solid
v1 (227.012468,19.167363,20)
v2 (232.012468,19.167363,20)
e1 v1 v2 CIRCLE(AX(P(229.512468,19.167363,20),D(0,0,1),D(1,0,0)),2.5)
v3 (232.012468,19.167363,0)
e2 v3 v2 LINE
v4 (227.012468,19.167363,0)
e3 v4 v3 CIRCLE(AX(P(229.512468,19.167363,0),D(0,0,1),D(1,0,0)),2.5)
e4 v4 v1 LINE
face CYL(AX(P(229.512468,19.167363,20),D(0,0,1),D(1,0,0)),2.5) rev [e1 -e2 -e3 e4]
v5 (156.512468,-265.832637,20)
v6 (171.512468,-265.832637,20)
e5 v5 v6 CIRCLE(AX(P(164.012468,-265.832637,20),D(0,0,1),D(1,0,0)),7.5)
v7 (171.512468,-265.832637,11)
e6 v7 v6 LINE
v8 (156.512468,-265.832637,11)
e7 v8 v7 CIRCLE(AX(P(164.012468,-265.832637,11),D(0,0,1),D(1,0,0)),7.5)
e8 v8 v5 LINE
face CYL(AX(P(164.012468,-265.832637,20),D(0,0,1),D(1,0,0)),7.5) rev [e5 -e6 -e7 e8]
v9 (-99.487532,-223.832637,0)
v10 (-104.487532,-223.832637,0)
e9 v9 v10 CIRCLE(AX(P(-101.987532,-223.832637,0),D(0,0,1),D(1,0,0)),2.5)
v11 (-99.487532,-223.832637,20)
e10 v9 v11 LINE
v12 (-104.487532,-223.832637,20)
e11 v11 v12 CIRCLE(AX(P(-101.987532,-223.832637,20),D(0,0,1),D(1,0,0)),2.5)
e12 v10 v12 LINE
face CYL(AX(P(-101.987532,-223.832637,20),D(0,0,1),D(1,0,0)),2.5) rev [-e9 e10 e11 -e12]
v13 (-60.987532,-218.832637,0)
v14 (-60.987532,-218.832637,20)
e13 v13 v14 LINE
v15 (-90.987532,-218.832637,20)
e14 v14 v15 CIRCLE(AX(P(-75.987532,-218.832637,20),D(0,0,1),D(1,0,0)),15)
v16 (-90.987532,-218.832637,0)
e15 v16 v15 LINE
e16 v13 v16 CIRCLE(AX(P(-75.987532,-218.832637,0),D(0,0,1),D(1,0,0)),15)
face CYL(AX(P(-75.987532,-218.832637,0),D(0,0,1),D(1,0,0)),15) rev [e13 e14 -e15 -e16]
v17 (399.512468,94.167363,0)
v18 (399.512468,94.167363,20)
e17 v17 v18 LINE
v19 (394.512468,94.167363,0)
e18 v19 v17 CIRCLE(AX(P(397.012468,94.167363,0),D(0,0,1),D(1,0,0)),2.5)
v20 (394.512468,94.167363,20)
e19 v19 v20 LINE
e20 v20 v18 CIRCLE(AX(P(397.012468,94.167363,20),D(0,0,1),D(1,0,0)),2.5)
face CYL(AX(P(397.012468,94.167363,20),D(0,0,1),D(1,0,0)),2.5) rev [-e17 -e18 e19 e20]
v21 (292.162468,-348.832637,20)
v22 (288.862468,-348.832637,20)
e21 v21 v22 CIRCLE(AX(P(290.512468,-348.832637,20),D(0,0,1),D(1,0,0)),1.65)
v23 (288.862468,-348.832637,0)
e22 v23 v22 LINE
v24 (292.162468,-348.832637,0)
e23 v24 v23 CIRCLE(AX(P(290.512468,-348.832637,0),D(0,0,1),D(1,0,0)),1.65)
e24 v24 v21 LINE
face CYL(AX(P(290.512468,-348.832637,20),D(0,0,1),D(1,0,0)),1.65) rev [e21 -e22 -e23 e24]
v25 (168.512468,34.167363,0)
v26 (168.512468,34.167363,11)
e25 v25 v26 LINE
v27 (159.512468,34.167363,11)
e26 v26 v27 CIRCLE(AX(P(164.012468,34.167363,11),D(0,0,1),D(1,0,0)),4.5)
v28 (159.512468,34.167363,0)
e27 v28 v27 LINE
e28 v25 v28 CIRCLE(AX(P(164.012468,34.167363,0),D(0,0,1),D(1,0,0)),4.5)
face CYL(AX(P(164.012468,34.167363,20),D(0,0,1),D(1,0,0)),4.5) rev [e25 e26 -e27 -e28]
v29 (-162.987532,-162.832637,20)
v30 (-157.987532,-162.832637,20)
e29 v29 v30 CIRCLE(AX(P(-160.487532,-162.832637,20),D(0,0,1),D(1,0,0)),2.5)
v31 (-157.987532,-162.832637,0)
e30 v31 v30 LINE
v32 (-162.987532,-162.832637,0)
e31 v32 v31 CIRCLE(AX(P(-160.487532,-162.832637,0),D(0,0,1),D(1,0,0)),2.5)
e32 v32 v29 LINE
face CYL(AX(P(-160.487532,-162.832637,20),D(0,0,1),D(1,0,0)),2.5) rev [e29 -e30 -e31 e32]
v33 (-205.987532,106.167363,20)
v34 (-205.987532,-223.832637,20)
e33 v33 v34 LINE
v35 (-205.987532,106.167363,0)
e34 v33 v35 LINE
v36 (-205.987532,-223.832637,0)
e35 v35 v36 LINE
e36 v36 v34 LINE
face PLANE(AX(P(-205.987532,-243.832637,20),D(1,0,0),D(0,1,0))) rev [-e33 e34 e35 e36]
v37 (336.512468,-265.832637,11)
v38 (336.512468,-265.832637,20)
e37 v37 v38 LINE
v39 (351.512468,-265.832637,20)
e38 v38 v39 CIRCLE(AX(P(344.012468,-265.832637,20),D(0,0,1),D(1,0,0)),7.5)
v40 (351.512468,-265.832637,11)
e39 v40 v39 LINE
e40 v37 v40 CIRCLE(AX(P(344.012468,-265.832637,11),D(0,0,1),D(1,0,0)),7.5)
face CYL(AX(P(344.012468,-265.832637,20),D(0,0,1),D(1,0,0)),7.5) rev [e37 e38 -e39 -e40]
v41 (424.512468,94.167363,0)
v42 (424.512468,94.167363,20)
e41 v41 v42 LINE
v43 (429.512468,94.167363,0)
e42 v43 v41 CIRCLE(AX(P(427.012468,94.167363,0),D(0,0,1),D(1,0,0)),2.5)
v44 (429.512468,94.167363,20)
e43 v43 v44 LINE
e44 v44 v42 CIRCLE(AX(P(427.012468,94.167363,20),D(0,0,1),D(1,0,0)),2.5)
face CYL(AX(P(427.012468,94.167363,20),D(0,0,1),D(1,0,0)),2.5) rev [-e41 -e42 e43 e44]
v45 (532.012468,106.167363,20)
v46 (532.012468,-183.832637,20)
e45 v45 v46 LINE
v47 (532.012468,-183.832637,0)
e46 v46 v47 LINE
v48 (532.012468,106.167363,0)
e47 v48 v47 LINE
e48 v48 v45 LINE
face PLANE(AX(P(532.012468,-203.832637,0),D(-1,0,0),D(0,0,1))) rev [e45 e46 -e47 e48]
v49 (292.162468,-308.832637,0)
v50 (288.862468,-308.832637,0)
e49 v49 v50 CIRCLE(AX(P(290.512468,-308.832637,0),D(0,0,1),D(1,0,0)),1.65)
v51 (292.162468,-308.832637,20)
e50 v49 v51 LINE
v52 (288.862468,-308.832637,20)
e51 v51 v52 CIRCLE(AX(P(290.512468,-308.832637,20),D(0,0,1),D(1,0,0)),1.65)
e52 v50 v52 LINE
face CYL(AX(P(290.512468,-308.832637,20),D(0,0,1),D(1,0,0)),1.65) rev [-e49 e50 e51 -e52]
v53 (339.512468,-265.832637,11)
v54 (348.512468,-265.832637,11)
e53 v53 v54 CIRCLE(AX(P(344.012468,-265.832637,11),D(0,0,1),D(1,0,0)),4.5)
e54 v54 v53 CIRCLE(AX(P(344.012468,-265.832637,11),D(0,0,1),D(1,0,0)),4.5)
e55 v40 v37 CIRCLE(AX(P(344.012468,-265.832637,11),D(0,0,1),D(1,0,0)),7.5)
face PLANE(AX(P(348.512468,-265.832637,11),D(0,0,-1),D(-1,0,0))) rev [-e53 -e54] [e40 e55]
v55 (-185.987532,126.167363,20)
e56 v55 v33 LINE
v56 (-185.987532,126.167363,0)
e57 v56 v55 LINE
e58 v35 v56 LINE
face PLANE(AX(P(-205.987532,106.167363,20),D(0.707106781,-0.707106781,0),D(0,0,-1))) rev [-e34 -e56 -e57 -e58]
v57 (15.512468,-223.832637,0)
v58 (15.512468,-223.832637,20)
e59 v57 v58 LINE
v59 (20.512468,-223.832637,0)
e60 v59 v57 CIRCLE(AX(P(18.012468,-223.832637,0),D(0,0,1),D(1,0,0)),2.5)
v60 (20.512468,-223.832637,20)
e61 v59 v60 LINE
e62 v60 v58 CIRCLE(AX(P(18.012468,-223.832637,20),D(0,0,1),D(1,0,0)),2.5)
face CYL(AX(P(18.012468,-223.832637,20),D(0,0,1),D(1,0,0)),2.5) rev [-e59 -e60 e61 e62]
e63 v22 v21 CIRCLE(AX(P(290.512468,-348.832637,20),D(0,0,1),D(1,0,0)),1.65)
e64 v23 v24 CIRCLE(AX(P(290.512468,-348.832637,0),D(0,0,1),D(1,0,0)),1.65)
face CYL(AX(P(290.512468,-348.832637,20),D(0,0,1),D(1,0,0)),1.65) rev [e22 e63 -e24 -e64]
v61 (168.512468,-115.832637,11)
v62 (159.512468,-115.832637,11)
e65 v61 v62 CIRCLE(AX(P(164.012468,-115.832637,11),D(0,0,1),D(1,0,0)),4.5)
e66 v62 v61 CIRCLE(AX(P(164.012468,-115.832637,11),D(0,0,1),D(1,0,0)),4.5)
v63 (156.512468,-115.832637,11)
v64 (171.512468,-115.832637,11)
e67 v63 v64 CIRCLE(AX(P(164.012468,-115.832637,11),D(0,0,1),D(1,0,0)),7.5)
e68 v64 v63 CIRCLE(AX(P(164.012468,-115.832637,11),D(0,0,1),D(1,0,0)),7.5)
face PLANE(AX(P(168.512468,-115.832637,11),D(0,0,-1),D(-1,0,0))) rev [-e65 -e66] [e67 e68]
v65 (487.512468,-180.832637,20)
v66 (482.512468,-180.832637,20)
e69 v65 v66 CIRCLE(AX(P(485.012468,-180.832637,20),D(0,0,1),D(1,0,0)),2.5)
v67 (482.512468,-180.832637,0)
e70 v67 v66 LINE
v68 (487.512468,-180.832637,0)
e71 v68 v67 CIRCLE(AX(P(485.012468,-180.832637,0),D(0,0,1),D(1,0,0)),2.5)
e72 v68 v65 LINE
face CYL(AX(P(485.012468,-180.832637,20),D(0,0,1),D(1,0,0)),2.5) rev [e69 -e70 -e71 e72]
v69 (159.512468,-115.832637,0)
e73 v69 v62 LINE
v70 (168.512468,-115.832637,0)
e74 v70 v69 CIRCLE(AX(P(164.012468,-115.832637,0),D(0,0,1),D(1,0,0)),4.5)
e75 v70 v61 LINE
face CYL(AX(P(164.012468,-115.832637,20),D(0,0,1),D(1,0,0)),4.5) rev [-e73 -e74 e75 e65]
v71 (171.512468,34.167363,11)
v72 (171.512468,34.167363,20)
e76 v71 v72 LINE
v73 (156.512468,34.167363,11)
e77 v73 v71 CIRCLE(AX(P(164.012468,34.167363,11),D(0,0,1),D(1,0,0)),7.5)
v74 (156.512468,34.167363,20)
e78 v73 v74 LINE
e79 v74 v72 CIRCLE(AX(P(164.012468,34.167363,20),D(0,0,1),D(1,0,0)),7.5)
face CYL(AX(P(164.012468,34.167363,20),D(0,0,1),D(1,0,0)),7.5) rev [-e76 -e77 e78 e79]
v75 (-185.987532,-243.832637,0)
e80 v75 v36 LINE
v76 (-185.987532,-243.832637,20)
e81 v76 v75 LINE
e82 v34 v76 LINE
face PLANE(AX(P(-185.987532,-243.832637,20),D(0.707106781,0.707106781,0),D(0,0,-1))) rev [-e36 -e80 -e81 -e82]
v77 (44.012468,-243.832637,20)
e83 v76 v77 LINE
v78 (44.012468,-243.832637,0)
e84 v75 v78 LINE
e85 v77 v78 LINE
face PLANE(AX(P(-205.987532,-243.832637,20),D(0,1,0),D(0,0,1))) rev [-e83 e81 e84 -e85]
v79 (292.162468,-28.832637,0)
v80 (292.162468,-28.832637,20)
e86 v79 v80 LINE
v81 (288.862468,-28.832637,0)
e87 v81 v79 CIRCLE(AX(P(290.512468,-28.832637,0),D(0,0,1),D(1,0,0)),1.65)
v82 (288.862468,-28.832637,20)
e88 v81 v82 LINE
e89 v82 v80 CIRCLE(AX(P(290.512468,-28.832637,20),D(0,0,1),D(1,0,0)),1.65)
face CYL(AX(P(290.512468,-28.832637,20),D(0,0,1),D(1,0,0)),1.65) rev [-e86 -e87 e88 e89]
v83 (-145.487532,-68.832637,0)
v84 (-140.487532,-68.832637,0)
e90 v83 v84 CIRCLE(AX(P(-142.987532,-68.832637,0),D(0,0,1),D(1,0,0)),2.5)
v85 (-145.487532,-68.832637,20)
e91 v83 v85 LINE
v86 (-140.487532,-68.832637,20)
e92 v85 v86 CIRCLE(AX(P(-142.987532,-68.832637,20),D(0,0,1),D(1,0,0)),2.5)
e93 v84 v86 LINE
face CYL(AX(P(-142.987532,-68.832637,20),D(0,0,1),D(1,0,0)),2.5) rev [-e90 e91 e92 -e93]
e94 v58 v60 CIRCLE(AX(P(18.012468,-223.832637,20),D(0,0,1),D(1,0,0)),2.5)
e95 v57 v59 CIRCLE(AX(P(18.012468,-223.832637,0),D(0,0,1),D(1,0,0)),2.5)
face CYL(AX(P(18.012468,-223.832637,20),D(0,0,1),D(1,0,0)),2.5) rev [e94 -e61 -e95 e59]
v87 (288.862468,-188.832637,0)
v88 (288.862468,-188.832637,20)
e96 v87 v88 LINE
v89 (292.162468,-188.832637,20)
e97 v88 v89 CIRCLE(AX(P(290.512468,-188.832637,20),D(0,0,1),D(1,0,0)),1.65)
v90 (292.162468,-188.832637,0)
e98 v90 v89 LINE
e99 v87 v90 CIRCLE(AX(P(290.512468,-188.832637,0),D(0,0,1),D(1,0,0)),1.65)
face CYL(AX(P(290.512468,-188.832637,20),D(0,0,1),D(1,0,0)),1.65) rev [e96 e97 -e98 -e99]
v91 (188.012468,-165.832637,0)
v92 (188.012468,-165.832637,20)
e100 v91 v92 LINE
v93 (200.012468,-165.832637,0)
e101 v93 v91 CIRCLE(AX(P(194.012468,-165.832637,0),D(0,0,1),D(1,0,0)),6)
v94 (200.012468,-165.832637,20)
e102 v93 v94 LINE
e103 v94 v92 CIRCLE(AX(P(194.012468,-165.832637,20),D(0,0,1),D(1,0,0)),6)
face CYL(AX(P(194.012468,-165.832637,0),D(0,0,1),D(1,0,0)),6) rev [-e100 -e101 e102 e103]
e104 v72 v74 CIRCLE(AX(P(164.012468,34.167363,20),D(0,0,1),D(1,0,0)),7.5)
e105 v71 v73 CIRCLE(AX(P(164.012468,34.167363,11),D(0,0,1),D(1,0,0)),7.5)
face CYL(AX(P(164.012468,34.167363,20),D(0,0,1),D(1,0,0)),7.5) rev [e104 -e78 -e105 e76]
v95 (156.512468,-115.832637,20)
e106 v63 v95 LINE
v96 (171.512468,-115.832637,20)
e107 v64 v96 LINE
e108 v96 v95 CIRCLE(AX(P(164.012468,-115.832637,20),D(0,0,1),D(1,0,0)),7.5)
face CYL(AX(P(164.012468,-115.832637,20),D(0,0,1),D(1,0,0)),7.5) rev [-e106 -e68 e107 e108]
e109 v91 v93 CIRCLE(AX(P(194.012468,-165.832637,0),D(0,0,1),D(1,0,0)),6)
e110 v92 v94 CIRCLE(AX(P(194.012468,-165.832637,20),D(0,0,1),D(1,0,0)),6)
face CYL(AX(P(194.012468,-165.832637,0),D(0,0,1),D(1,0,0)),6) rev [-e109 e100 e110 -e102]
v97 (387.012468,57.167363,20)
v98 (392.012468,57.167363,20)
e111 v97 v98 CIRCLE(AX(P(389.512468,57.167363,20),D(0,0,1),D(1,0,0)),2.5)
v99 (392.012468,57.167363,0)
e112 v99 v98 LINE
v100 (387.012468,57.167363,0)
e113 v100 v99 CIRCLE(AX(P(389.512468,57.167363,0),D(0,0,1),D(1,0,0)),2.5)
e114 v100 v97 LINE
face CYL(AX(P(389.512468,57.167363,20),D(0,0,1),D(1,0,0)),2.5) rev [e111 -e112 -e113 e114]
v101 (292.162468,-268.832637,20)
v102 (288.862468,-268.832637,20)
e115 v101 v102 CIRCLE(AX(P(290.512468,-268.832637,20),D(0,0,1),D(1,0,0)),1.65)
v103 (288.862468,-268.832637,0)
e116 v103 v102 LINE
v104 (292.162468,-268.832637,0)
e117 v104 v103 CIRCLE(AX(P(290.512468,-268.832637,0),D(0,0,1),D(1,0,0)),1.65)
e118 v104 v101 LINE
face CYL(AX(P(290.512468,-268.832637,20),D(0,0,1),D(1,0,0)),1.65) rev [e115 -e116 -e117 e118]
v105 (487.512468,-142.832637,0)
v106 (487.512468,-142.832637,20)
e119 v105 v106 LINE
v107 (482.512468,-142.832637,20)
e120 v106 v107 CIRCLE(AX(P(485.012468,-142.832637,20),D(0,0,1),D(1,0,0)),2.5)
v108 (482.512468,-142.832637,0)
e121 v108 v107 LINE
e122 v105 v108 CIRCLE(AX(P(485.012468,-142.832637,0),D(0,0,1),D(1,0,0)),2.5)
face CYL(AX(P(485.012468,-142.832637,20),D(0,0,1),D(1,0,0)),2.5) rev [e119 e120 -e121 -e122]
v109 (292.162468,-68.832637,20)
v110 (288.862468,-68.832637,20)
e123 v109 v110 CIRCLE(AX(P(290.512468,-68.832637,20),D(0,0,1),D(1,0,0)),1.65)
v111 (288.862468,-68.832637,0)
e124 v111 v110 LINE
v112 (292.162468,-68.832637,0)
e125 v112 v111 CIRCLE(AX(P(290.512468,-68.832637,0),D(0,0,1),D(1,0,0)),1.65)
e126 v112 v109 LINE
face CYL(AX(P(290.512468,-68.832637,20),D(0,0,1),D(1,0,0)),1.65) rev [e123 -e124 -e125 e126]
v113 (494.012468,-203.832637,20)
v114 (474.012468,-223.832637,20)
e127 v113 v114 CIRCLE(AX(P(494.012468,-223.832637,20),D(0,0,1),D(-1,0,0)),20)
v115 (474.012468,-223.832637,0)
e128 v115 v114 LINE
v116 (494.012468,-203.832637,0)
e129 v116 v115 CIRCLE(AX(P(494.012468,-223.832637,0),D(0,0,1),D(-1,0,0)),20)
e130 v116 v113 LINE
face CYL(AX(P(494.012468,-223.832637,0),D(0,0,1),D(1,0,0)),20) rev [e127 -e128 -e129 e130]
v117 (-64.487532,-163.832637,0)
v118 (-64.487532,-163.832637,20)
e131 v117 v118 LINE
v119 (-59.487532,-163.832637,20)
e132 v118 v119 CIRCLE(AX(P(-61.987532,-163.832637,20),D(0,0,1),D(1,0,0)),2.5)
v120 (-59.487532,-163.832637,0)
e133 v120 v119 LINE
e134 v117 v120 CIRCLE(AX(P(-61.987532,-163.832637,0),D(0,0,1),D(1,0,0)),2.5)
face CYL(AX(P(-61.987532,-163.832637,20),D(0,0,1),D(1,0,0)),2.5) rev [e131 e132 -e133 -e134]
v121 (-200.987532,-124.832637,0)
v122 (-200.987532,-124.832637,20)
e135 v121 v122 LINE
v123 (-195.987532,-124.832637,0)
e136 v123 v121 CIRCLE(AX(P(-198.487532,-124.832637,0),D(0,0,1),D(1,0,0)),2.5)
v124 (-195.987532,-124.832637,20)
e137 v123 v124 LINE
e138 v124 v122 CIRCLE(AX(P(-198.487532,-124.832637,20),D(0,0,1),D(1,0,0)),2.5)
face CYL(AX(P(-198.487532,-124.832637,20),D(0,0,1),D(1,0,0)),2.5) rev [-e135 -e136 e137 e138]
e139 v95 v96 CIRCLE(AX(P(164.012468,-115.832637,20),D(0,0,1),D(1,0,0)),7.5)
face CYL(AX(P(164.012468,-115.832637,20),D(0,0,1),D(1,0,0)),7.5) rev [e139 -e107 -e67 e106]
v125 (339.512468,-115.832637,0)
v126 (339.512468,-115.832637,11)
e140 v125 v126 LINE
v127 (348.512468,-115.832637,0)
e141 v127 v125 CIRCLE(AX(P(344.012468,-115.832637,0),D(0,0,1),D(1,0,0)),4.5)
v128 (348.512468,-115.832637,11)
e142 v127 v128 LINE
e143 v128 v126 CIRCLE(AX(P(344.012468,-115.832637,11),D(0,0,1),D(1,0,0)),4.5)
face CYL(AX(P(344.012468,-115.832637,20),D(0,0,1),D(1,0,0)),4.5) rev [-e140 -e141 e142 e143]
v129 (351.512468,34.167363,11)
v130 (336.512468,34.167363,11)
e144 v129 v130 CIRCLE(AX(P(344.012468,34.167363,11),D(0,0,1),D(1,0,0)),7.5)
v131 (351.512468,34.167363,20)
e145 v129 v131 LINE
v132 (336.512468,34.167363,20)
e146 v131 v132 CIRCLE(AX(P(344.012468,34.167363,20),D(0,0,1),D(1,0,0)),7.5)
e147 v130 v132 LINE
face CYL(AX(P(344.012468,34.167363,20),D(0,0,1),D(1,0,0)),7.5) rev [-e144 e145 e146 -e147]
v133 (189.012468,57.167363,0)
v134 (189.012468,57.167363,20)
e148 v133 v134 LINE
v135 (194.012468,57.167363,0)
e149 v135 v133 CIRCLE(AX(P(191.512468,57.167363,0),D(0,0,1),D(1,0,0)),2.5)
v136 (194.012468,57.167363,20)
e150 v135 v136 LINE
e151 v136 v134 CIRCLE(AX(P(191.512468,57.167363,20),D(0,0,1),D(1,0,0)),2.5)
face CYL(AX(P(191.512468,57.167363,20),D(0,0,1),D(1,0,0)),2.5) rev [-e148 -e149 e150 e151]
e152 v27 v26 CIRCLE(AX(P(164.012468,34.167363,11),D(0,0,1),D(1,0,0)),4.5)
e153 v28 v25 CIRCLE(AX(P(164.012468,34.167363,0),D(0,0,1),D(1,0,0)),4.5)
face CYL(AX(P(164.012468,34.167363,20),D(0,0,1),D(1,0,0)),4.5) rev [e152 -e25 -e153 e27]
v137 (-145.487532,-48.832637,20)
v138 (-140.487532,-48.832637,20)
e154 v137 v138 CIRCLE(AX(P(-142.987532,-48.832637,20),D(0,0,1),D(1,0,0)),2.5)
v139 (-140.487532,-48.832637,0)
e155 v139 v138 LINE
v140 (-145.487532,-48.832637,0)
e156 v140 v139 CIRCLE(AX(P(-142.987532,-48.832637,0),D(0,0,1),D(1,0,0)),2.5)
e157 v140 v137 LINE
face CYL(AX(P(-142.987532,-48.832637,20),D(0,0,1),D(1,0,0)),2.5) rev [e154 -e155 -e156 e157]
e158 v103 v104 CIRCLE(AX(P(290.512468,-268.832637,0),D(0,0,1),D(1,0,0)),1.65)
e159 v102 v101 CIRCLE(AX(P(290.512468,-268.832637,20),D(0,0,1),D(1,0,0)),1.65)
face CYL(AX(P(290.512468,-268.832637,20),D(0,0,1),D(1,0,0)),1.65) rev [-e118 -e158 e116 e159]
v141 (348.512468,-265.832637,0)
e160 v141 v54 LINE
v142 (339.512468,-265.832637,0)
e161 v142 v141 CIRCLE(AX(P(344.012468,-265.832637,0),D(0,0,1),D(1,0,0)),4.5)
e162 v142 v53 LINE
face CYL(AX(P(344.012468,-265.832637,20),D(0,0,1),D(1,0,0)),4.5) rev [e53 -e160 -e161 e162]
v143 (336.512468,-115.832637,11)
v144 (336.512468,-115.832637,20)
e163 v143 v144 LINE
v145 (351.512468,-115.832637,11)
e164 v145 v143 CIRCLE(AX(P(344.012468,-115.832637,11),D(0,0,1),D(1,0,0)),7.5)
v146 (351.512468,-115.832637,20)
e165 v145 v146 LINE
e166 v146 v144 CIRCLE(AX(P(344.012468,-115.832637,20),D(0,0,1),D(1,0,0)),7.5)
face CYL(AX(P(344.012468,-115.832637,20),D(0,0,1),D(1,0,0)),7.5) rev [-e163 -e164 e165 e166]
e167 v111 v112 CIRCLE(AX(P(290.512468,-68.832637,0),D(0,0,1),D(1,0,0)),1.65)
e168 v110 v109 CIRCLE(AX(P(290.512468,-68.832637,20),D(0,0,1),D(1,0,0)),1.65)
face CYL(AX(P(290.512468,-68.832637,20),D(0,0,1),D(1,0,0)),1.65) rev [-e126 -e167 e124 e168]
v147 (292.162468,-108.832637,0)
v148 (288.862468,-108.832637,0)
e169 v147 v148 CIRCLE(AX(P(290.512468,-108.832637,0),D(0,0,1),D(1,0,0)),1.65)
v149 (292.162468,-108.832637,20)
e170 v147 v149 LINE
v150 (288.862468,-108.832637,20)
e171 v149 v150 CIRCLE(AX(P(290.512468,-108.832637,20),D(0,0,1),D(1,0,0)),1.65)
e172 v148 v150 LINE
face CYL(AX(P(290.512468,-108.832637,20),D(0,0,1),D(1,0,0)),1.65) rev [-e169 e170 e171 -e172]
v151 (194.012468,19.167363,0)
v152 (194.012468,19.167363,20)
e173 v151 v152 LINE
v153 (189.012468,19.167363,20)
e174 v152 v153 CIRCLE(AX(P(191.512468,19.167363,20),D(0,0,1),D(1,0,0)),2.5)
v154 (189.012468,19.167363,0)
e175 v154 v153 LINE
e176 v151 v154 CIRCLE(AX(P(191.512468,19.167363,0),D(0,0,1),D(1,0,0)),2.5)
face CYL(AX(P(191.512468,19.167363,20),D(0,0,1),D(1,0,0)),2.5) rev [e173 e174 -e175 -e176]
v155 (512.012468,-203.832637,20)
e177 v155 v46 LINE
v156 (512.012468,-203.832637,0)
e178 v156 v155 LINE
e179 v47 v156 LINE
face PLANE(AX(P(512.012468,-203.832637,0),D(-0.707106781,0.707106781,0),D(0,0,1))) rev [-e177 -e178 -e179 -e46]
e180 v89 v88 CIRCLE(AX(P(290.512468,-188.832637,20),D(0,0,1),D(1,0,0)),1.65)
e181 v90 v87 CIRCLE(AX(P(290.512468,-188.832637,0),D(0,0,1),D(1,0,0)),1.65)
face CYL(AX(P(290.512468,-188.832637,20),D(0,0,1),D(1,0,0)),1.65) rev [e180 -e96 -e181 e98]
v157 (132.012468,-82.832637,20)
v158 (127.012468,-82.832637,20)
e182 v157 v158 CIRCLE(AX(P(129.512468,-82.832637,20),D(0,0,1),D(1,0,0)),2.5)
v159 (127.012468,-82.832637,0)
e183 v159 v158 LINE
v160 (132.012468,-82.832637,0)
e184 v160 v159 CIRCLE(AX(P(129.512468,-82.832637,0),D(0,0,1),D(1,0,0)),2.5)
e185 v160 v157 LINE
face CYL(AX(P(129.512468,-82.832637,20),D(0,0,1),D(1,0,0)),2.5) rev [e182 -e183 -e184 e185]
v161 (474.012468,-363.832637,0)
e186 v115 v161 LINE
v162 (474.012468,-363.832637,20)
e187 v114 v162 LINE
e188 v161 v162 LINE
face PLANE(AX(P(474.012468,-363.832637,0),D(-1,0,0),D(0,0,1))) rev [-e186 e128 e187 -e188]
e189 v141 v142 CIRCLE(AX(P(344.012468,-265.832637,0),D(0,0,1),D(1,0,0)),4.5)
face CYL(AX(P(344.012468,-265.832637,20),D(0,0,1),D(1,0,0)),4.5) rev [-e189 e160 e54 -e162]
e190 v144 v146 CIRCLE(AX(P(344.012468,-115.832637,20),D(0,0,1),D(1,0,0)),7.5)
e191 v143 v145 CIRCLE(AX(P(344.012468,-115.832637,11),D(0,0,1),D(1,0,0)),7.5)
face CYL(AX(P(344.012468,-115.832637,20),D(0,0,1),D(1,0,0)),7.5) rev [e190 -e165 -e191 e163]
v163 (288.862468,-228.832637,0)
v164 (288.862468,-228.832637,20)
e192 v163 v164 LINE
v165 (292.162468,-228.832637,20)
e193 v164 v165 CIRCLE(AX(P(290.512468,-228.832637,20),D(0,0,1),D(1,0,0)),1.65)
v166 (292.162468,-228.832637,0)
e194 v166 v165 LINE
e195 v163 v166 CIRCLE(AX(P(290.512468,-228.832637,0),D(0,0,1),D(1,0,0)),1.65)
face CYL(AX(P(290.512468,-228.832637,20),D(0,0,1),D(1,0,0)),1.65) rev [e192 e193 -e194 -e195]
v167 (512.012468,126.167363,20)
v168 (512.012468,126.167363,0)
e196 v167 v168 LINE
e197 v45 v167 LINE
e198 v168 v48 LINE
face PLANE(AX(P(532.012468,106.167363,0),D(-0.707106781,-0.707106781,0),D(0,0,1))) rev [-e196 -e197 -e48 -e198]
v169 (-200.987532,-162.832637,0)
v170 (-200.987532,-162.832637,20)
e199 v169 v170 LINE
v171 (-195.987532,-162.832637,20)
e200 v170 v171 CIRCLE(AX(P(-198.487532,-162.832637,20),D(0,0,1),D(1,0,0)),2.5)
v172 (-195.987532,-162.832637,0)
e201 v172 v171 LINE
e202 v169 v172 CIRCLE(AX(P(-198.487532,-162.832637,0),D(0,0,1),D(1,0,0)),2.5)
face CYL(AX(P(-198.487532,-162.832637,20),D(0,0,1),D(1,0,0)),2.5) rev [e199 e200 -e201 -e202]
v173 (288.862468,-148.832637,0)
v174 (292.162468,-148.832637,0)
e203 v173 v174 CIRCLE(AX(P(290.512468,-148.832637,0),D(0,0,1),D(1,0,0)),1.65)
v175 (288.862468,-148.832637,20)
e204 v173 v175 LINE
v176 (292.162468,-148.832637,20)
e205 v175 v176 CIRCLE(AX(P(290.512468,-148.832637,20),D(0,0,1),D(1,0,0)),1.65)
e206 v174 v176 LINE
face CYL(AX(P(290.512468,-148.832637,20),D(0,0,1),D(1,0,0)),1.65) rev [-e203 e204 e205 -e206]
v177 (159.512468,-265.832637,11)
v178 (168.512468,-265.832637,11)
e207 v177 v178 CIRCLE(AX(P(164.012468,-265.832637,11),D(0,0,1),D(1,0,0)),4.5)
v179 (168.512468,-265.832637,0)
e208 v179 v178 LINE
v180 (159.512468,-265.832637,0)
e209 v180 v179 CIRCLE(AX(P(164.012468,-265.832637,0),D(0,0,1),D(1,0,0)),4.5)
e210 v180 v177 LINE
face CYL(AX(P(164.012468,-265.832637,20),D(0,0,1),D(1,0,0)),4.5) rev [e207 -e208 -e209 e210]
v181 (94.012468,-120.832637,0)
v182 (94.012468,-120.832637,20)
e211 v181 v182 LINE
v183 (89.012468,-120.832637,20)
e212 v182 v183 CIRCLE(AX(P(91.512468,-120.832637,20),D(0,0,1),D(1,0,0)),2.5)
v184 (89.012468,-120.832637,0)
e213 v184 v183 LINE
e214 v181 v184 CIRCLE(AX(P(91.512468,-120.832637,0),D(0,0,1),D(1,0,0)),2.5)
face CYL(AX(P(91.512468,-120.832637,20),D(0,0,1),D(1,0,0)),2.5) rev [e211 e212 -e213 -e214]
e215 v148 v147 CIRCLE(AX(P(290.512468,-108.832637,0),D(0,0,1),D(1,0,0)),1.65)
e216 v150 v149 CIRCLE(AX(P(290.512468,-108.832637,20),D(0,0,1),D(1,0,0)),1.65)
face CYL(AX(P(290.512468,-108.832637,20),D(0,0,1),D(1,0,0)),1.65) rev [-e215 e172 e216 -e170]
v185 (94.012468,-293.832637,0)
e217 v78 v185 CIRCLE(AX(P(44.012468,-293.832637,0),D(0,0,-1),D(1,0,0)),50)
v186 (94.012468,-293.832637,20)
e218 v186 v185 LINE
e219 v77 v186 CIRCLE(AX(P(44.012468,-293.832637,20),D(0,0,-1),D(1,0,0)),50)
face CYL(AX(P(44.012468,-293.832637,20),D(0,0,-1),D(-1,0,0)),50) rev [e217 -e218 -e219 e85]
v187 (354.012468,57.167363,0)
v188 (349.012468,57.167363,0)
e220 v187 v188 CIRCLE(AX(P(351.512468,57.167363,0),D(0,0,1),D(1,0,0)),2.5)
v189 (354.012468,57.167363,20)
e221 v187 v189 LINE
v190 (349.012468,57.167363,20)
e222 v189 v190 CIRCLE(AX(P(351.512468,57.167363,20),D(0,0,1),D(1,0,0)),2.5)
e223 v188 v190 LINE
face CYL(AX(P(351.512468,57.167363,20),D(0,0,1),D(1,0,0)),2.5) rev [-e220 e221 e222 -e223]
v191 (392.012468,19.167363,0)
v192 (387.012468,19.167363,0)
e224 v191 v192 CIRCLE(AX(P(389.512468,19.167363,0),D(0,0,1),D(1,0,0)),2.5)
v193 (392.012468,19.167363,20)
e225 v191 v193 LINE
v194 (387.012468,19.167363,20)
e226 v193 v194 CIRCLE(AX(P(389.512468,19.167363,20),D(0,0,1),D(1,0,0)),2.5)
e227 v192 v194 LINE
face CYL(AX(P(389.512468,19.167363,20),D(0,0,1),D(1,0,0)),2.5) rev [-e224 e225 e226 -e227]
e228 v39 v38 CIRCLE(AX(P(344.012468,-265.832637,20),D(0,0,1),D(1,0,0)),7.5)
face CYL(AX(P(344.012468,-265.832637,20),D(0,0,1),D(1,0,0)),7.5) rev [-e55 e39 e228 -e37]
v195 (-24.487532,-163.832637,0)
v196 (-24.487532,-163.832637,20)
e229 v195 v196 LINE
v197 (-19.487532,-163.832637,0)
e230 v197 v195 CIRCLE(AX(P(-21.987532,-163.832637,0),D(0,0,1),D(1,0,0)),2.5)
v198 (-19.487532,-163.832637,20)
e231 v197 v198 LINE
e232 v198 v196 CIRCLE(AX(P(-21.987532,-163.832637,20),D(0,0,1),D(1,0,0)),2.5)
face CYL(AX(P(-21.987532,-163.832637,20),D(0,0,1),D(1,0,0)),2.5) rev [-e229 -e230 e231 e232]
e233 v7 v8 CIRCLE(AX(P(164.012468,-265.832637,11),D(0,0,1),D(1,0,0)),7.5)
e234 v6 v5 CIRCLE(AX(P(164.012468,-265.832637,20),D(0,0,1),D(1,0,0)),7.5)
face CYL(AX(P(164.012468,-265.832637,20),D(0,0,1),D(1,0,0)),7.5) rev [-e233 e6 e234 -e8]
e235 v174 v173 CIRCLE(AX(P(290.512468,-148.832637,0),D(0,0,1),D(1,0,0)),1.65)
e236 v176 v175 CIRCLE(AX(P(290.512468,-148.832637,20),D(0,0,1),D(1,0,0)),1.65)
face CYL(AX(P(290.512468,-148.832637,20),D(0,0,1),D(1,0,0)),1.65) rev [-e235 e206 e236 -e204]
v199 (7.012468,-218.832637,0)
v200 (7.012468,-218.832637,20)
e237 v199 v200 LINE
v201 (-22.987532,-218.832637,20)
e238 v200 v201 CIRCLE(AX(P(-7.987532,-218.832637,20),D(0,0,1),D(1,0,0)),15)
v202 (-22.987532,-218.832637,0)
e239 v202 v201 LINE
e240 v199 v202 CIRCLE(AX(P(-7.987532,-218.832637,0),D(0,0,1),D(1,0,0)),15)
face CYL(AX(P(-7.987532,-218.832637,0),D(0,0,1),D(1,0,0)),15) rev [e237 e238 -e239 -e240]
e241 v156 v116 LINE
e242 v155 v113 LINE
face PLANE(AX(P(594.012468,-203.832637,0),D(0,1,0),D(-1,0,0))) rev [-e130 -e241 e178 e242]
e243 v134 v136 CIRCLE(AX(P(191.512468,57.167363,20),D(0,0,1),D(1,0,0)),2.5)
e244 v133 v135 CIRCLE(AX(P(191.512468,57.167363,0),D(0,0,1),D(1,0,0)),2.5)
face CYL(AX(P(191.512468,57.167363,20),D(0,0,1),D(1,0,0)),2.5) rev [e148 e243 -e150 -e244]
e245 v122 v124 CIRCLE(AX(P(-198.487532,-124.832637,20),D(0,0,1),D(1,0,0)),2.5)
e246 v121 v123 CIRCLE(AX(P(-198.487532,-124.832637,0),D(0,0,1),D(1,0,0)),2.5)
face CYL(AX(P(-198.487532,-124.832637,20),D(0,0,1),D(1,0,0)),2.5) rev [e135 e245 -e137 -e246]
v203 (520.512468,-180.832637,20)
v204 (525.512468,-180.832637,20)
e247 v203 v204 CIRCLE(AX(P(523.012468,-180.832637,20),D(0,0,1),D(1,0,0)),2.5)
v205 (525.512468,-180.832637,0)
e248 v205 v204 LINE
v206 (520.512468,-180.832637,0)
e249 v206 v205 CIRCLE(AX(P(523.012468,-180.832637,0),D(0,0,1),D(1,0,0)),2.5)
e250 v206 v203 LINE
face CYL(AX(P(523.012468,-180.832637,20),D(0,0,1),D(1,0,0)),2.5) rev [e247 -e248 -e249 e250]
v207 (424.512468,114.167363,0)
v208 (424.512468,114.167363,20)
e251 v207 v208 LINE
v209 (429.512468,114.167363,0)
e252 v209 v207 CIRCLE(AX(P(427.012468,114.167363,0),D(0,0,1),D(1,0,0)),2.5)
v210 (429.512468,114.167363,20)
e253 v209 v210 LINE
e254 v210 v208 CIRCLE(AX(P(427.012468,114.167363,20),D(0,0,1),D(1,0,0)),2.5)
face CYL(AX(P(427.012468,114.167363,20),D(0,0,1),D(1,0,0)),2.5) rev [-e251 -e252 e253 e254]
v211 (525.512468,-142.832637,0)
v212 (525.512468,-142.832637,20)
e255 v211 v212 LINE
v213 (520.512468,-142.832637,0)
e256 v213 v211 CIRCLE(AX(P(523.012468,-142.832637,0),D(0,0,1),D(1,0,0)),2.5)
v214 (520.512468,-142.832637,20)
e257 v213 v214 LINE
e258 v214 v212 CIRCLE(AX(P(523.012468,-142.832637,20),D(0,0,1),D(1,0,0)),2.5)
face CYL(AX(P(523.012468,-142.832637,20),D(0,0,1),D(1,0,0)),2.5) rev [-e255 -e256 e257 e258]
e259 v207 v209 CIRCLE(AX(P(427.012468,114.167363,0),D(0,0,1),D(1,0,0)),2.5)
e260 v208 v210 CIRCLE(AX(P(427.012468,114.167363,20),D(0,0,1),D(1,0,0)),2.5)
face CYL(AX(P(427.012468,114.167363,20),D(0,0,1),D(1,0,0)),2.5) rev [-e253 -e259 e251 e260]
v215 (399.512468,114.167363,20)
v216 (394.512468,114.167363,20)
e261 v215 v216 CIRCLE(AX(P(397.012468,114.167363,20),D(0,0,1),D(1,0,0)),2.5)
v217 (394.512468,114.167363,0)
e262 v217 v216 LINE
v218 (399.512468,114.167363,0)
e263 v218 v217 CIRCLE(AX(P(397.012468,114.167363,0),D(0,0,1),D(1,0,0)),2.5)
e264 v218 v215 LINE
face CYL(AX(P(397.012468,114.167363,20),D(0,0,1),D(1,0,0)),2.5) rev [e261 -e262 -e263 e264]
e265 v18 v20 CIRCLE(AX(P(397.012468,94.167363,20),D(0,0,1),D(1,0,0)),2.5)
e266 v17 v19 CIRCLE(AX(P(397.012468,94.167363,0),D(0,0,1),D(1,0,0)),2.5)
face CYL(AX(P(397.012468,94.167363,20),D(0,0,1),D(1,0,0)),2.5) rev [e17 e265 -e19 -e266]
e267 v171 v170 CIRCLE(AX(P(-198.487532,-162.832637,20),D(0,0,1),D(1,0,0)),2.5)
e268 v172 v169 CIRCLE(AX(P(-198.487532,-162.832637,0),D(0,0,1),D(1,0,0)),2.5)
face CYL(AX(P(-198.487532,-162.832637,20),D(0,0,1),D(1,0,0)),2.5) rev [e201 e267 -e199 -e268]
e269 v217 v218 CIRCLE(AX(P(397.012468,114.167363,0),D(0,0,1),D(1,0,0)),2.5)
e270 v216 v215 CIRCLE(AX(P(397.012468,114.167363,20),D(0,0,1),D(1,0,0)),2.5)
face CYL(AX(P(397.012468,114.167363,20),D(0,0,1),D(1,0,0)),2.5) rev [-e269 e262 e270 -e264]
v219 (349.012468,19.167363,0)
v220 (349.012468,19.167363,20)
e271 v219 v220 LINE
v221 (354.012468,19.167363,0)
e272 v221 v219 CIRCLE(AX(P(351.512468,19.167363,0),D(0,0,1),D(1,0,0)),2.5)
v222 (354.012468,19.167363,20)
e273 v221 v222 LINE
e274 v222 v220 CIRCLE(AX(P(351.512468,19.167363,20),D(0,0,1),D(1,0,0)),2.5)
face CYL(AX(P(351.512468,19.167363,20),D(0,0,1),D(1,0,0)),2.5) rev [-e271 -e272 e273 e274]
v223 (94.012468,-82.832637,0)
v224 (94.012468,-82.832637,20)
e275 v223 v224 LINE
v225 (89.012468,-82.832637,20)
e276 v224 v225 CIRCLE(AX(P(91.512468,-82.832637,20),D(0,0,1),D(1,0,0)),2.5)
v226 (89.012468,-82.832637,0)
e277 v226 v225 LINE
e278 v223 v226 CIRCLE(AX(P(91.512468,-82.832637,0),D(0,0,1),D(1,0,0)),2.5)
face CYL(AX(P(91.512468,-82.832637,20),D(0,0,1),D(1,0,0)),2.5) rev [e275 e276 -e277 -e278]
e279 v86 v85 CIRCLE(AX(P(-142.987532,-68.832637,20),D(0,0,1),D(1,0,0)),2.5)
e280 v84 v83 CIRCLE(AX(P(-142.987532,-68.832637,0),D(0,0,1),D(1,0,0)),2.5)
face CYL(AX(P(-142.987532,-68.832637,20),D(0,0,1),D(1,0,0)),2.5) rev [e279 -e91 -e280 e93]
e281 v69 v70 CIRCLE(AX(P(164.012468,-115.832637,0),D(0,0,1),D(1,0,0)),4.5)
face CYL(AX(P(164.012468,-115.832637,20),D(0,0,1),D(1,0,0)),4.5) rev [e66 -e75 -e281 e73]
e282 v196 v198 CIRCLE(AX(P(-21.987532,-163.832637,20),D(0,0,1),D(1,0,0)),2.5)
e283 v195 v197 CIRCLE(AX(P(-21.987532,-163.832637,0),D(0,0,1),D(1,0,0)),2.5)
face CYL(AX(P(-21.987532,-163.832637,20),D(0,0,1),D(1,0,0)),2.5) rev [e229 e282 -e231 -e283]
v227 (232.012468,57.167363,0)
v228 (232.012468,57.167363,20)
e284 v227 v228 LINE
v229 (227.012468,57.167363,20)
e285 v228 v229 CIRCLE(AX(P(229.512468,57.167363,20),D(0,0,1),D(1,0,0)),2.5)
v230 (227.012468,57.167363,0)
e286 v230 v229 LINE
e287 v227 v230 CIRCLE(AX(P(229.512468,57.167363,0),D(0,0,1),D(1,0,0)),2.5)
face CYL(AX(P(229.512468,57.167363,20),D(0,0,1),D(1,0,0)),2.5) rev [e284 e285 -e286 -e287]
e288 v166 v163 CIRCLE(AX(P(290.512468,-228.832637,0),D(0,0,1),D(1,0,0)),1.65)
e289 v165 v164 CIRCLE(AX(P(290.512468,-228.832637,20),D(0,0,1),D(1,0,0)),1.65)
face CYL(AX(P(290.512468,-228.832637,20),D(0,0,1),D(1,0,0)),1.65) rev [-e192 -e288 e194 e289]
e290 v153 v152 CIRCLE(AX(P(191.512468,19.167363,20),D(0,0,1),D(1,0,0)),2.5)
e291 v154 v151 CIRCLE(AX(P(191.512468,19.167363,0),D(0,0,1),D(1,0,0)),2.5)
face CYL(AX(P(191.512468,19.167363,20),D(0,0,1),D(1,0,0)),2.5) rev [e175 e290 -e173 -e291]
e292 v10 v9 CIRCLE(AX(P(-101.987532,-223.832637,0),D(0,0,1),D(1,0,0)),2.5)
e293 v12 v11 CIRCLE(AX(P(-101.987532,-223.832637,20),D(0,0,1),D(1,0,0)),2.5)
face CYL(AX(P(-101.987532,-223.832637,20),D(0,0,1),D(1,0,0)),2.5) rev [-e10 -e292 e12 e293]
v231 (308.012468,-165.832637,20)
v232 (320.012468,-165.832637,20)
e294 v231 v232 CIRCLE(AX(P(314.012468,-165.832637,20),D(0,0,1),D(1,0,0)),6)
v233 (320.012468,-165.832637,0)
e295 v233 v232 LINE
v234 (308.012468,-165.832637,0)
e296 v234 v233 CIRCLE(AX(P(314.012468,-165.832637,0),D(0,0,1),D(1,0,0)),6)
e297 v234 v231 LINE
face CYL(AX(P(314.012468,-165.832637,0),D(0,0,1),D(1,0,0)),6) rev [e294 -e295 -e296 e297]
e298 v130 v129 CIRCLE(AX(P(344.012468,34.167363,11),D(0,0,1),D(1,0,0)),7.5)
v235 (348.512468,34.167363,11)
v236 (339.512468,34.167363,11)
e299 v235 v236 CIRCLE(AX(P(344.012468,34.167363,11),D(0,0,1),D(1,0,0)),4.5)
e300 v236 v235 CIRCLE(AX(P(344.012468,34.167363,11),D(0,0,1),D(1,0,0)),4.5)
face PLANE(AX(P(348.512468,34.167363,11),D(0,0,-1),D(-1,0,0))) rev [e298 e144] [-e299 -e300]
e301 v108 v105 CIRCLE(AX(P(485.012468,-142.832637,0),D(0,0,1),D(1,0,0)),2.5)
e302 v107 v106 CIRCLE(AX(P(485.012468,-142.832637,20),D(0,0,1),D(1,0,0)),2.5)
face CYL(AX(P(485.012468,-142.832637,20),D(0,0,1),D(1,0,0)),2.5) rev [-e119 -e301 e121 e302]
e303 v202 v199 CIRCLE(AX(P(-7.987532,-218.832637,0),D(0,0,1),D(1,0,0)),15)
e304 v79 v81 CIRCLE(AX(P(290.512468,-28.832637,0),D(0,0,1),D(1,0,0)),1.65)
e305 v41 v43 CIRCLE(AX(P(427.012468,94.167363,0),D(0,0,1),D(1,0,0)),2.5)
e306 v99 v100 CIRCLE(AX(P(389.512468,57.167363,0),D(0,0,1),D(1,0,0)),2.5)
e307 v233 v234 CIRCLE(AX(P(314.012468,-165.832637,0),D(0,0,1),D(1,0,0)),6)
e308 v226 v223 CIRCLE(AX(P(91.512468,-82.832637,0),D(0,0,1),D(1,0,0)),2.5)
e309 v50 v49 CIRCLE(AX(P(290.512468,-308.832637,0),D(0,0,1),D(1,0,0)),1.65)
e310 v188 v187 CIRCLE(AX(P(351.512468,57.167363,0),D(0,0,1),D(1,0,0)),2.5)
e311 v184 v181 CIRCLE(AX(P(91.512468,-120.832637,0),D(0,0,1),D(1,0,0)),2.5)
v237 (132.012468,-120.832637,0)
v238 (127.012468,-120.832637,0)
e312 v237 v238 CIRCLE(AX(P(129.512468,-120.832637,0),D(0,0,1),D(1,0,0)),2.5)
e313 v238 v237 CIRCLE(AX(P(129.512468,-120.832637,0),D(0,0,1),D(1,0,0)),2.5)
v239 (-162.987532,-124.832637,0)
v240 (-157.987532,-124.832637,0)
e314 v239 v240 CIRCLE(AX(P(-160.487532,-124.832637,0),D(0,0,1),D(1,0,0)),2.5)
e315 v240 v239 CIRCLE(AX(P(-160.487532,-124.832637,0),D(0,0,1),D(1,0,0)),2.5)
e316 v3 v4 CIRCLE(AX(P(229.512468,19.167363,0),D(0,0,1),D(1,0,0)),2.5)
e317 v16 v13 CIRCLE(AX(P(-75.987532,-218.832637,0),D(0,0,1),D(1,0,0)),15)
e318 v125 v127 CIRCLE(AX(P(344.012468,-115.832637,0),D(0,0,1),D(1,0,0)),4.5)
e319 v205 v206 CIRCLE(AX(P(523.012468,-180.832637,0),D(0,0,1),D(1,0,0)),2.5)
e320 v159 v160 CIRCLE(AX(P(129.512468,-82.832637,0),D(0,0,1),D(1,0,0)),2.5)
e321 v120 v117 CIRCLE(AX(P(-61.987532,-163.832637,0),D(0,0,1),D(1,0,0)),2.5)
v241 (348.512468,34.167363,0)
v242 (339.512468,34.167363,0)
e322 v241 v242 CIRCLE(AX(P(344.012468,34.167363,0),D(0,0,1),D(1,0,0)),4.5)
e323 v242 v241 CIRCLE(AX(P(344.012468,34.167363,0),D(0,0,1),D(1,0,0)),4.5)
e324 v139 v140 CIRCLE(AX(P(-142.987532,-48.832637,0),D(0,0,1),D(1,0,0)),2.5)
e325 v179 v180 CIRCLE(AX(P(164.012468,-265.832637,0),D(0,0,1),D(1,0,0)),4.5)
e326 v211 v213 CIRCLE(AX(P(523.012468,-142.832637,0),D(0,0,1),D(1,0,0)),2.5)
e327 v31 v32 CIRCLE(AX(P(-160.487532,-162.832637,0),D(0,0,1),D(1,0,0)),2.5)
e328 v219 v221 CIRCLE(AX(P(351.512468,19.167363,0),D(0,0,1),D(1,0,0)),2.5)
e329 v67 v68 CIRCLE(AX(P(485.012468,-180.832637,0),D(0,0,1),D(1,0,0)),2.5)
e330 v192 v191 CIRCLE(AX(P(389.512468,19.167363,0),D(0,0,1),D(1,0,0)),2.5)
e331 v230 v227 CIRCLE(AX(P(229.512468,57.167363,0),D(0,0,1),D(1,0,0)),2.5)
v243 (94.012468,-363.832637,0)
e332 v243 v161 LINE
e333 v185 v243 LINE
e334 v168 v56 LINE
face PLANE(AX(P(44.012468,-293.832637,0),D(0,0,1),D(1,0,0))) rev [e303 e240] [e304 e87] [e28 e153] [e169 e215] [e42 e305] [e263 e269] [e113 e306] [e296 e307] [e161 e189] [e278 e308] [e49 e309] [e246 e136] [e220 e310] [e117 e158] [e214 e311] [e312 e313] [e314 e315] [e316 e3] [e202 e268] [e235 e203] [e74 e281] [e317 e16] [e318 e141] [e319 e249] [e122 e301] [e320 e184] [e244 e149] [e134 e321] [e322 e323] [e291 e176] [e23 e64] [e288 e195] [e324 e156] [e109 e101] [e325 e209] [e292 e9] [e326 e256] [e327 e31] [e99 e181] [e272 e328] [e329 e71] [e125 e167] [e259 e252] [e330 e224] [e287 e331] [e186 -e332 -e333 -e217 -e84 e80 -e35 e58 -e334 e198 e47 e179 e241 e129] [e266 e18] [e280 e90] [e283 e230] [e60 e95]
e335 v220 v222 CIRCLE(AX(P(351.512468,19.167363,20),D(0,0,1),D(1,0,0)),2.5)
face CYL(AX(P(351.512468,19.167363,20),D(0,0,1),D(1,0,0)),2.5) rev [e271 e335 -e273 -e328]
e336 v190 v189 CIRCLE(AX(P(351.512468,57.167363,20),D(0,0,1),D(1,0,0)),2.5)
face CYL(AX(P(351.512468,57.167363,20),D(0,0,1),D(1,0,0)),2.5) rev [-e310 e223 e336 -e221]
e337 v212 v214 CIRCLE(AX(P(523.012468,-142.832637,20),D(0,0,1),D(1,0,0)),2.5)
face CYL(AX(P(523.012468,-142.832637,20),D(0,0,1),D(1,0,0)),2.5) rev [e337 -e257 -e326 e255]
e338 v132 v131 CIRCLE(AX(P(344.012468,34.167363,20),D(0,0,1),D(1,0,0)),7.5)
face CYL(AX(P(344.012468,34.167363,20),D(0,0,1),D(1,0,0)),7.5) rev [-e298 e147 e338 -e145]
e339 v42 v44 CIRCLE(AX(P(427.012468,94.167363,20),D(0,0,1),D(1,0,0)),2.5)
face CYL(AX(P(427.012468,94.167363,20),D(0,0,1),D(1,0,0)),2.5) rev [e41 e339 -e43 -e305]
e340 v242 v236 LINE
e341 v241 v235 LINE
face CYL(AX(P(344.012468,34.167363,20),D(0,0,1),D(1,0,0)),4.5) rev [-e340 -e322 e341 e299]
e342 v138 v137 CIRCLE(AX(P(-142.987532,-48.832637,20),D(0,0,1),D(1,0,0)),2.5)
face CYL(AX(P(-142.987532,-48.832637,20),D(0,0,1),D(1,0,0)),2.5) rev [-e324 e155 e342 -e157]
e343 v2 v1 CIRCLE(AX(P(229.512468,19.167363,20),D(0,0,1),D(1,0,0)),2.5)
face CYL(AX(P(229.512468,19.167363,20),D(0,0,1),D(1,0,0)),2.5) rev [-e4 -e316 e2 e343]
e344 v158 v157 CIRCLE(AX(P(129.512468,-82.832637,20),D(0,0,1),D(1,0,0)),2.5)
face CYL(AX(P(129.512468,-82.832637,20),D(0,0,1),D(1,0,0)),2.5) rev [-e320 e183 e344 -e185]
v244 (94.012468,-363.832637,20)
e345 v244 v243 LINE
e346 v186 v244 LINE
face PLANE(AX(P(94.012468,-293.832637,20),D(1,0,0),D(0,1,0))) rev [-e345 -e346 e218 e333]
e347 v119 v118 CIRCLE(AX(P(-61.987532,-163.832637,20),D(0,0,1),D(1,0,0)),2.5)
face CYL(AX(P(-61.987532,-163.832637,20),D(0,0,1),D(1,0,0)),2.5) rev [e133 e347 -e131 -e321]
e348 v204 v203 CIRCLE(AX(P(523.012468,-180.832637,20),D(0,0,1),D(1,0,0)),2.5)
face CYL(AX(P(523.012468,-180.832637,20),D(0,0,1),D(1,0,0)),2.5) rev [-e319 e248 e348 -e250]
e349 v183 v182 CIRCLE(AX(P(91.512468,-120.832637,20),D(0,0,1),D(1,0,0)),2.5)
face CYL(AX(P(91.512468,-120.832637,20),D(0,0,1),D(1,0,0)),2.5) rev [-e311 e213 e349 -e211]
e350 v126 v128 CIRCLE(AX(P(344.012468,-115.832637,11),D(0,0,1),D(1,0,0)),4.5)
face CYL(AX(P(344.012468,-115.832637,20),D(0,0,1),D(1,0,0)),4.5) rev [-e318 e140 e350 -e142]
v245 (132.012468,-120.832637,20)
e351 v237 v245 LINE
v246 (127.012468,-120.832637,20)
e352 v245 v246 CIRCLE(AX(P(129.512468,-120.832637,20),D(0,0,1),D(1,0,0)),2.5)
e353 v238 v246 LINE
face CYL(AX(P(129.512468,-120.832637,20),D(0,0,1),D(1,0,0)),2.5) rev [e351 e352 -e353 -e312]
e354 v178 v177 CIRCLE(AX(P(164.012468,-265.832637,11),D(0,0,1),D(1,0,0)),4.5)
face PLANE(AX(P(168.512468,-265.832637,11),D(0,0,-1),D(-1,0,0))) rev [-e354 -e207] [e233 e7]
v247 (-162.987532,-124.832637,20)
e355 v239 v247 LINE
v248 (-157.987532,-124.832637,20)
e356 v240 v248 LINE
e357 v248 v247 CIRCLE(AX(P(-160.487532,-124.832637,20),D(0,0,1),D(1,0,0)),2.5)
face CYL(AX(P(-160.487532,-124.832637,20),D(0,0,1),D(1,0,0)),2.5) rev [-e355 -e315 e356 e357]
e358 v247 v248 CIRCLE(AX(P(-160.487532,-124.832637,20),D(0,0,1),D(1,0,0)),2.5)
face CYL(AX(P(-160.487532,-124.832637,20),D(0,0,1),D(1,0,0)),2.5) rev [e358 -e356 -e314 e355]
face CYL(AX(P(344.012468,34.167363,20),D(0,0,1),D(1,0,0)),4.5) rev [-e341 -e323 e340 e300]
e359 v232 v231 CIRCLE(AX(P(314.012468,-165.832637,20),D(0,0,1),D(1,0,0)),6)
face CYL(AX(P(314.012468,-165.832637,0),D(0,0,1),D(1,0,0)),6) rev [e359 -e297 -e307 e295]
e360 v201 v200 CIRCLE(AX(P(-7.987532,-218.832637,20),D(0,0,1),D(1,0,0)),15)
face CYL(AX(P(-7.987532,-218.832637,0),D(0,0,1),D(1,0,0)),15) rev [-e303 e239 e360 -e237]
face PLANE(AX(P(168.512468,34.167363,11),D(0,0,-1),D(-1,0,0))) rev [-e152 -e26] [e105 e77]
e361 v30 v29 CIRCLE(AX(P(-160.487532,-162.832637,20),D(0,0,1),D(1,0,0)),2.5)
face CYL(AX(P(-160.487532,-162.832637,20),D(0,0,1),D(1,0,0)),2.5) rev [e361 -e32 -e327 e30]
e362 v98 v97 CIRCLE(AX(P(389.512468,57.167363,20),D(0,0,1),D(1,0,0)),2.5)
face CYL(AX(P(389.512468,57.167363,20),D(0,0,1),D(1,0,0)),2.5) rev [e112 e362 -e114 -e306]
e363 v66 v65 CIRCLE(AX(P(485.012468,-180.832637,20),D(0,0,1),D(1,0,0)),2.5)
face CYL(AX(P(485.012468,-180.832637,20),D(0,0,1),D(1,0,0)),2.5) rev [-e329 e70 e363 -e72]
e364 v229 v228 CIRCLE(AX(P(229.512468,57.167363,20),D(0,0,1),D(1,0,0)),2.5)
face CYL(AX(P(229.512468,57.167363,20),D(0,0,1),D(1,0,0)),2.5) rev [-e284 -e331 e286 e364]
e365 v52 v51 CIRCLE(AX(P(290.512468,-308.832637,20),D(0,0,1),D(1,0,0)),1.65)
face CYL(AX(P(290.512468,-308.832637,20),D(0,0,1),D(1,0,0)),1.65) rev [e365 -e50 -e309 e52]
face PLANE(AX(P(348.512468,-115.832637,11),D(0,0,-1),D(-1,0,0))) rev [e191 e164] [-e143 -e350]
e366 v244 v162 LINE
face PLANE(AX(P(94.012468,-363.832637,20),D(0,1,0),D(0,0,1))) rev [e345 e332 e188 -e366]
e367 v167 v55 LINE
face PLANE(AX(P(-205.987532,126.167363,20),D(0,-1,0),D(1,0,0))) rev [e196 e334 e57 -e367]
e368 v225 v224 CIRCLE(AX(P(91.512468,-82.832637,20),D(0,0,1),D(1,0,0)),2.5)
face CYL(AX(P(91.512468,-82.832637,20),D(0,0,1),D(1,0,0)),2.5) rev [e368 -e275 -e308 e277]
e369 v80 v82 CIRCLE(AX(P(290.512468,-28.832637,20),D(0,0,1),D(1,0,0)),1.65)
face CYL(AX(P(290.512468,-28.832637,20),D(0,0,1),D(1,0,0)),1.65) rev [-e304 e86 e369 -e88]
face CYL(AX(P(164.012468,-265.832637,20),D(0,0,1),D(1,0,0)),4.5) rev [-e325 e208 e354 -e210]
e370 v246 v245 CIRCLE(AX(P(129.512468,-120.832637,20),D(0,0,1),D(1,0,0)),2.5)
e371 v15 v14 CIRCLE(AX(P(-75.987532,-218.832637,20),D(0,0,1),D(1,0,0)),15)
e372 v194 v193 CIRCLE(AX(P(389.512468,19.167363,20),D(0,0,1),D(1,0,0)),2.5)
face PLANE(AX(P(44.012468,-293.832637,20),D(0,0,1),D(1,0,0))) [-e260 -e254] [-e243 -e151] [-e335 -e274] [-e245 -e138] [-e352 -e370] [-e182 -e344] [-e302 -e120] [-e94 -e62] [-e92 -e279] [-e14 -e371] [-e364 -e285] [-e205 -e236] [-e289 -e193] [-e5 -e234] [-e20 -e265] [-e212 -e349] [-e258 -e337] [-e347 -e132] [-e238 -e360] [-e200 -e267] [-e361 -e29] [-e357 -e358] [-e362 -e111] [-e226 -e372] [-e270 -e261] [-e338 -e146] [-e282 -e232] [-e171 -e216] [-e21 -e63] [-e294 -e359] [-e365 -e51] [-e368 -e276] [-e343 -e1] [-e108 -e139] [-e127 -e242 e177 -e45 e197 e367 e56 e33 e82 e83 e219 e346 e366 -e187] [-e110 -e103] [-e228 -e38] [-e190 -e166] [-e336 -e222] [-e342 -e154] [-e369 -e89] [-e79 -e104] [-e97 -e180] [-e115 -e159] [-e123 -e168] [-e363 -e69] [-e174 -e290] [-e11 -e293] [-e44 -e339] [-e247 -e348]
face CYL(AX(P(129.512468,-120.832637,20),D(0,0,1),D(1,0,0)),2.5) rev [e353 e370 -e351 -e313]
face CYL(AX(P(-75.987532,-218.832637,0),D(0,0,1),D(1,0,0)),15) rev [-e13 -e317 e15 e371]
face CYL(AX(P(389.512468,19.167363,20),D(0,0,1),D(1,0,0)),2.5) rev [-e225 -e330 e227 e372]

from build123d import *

# Parameters (mm, degrees)
BOSS_EXTRUDE3_DEPTH                                  = 20
CHAMFER1_SIZE                                        = 20
CUT_EXTRUDE3_DEPTH                                   = 697.867993238
SKETCH6_W                                            = 62
SKETCH6_H                                            = 330
CUT_EXTRUDE4_DEPTH                                   = 697.867993238
CHAMFER3_SIZE                                        = 20
M6_TAPPED_HOLE1_D                                    = 5
M4_TAPPED_HOLE1_D                                    = 3.3
M6_TAPPED_HOLE2_D                                    = 5
SKETCH17_R                                           = 15
CUT_EXTRUDE5_DEPTH                                   = 645.83443917
HOLE_SIZE_PER_SOCKET_HEAD_CAP_SCREW_TYPE_D           = 9
HOLE_SIZE_PER_SOCKET_HEAD_CAP_SCREW_TYPE_CBORE_D     = 15
HOLE_SIZE_PER_SOCKET_HEAD_CAP_SCREW_TYPE_CBORE_DEPTH = 9
SKETCH20_R                                           = 6
CUT_EXTRUDE6_DEPTH                                   = 645.83443917
M6_TAPPED_HOLE3_D                                    = 5
M6_TAPPED_HOLE4_D                                    = 5


with BuildPart() as part:
    # Sketch2 → Boss-Extrude3 (new body)
    with BuildSketch(Plane.XY):
        with BuildLine():
            Line((-205.987531774, -243.832636788), (44.012468226, -243.832636788))
            ThreePointArc((44.012468226, -243.832636788), (79.367807285, -258.477297729), (94.012468226, -293.832636788))
            Line((94.012468226, -293.832636788), (94.012468226, -363.832636788))
            Line((94.012468226, -363.832636788), (594.012468226, -363.832636788))
            Line((594.012468226, -363.832636788), (594.012468226, 126.167363212))
            Line((594.012468226, 126.167363212), (-205.987531774, 126.167363212))
            Line((-205.987531774, 126.167363212), (-205.987531774, -243.832636788))
        make_face()
    extrude(amount=BOSS_EXTRUDE3_DEPTH)

    # Chamfer1
    chamfer1_edges = [part.edges().sort_by_distance(p)[0] for p in [
        (-205.987531774, -243.832636788, 10),
        (-205.987531774, 126.167363212, 10),
        (594.012468226, 126.167363212, 10),
    ]]
    chamfer(chamfer1_edges, length=CHAMFER1_SIZE)

    # Sketch5 → Cut-Extrude3 (cut, through all)
    with BuildSketch(Plane.XY.offset(20)):
        with BuildLine():
            Line((594.012468226, -363.832636788), (474.012468226, -363.832636788))
            Line((474.012468226, -363.832636788), (474.012468226, -223.832636788))
            ThreePointArc((474.012468226, -223.832636788), (479.870332602, -209.690501165), (494.012468226, -203.832636788))
            Line((494.012468226, -203.832636788), (594.012468226, -203.832636788))
            Line((594.012468226, -203.832636788), (594.012468226, -363.832636788))
        make_face()
    extrude(amount=-CUT_EXTRUDE3_DEPTH, mode=Mode.SUBTRACT)

    # Sketch6 → Cut-Extrude4 (cut, through all)
    with BuildSketch(Plane.XY.offset(20)):
        with Locations((563.012468226, -38.832636788)):
            Rectangle(SKETCH6_W, SKETCH6_H)
    extrude(amount=-CUT_EXTRUDE4_DEPTH, mode=Mode.SUBTRACT)

    # Chamfer3
    chamfer3_edges = [part.edges().sort_by_distance(p)[0] for p in [
        (532.012468226, -203.832636788, 10),
        (532.012468226, 126.167363212, 10),
    ]]
    chamfer(chamfer3_edges, length=CHAMFER3_SIZE)

    # M6 Tapped Hole1 (through all)
    with Locations(Plane.XY.offset(20)):
        with Locations((427.012468226, 114.167363212), (397.012468226, 114.167363212), (397.012468226, 94.167363212), (427.012468226, 94.167363212)):
            Hole(M6_TAPPED_HOLE1_D / 2)

    # M4 Tapped Hole1 (through all)
    with Locations(Plane.XY.offset(20)):
        with Locations((290.512468226, -348.832636788), (290.512468226, -308.832636788), (290.512468226, -268.832636788), (290.512468226, -228.832636788), (290.512468226, -188.832636788), (290.512468226, -148.832636788), (290.512468226, -108.832636788), (290.512468226, -68.832636788), (290.512468226, -28.832636788)):
            Hole(M4_TAPPED_HOLE1_D / 2)

    # M6 Tapped Hole2 (through all)
    with Locations(Plane.XY.offset(20)):
        with Locations((-61.987531774, -163.832636788), (-101.987531774, -223.832636788), (18.012468226, -223.832636788), (-21.987531774, -163.832636788)):
            Hole(M6_TAPPED_HOLE2_D / 2)

    # Sketch17 → Cut-Extrude5 (cut, through all)
    with BuildSketch(Plane.XY.offset(20)):
        with Locations((-75.987531774, -218.832636788)):
            Circle(SKETCH17_R)
        with Locations((-7.987531774, -218.832636788)):
            Circle(SKETCH17_R)
    extrude(amount=-CUT_EXTRUDE5_DEPTH, mode=Mode.SUBTRACT)

    # Hole size per socket head cap screw type 1 (through all)
    with Locations(Plane.XY.offset(20)):
        with Locations((164.012468226, 34.167363212), (344.012468226, 34.167363212), (344.012468226, -115.832636788), (164.012468226, -115.832636788), (164.012468226, -265.832636788), (344.012468226, -265.832636788)):
            CounterBoreHole(HOLE_SIZE_PER_SOCKET_HEAD_CAP_SCREW_TYPE_D / 2, HOLE_SIZE_PER_SOCKET_HEAD_CAP_SCREW_TYPE_CBORE_D / 2, HOLE_SIZE_PER_SOCKET_HEAD_CAP_SCREW_TYPE_CBORE_DEPTH)

    # Sketch20 → Cut-Extrude6 (cut, through all)
    with BuildSketch(Plane.XY.offset(20)):
        with Locations((194.012468226, -165.832636788)):
            Circle(SKETCH20_R)
        with Locations((314.012468226, -165.832636788)):
            Circle(SKETCH20_R)
    extrude(amount=-CUT_EXTRUDE6_DEPTH, mode=Mode.SUBTRACT)

    # M6 Tapped Hole3 (through all)
    with Locations(Plane.XY.offset(20)):
        with Locations((-198.487531774, -124.832636788), (-160.487531774, -124.832636788), (-160.487531774, -162.832636788), (-198.487531774, -162.832636788), (191.512468226, 19.167363212), (229.512468226, 19.167363212), (229.512468226, 57.167363212), (191.512468226, 57.167363212), (389.512468226, 19.167363212), (351.512468226, 19.167363212), (389.512468226, 57.167363212), (351.512468226, 57.167363212), (523.012468226, -142.832636788), (485.012468226, -142.832636788), (485.012468226, -180.832636788), (523.012468226, -180.832636788), (91.512468226, -82.832636788), (129.512468226, -82.832636788), (129.512468226, -120.832636788), (91.512468226, -120.832636788)):
            Hole(M6_TAPPED_HOLE3_D / 2)

    # M6 Tapped Hole4 (through all)
    with Locations(Plane.XY.offset(20)):
        with Locations((-142.987531774, -48.832636788), (-142.987531774, -68.832636788)):
            Hole(M6_TAPPED_HOLE4_D / 2)


solid = part.part
